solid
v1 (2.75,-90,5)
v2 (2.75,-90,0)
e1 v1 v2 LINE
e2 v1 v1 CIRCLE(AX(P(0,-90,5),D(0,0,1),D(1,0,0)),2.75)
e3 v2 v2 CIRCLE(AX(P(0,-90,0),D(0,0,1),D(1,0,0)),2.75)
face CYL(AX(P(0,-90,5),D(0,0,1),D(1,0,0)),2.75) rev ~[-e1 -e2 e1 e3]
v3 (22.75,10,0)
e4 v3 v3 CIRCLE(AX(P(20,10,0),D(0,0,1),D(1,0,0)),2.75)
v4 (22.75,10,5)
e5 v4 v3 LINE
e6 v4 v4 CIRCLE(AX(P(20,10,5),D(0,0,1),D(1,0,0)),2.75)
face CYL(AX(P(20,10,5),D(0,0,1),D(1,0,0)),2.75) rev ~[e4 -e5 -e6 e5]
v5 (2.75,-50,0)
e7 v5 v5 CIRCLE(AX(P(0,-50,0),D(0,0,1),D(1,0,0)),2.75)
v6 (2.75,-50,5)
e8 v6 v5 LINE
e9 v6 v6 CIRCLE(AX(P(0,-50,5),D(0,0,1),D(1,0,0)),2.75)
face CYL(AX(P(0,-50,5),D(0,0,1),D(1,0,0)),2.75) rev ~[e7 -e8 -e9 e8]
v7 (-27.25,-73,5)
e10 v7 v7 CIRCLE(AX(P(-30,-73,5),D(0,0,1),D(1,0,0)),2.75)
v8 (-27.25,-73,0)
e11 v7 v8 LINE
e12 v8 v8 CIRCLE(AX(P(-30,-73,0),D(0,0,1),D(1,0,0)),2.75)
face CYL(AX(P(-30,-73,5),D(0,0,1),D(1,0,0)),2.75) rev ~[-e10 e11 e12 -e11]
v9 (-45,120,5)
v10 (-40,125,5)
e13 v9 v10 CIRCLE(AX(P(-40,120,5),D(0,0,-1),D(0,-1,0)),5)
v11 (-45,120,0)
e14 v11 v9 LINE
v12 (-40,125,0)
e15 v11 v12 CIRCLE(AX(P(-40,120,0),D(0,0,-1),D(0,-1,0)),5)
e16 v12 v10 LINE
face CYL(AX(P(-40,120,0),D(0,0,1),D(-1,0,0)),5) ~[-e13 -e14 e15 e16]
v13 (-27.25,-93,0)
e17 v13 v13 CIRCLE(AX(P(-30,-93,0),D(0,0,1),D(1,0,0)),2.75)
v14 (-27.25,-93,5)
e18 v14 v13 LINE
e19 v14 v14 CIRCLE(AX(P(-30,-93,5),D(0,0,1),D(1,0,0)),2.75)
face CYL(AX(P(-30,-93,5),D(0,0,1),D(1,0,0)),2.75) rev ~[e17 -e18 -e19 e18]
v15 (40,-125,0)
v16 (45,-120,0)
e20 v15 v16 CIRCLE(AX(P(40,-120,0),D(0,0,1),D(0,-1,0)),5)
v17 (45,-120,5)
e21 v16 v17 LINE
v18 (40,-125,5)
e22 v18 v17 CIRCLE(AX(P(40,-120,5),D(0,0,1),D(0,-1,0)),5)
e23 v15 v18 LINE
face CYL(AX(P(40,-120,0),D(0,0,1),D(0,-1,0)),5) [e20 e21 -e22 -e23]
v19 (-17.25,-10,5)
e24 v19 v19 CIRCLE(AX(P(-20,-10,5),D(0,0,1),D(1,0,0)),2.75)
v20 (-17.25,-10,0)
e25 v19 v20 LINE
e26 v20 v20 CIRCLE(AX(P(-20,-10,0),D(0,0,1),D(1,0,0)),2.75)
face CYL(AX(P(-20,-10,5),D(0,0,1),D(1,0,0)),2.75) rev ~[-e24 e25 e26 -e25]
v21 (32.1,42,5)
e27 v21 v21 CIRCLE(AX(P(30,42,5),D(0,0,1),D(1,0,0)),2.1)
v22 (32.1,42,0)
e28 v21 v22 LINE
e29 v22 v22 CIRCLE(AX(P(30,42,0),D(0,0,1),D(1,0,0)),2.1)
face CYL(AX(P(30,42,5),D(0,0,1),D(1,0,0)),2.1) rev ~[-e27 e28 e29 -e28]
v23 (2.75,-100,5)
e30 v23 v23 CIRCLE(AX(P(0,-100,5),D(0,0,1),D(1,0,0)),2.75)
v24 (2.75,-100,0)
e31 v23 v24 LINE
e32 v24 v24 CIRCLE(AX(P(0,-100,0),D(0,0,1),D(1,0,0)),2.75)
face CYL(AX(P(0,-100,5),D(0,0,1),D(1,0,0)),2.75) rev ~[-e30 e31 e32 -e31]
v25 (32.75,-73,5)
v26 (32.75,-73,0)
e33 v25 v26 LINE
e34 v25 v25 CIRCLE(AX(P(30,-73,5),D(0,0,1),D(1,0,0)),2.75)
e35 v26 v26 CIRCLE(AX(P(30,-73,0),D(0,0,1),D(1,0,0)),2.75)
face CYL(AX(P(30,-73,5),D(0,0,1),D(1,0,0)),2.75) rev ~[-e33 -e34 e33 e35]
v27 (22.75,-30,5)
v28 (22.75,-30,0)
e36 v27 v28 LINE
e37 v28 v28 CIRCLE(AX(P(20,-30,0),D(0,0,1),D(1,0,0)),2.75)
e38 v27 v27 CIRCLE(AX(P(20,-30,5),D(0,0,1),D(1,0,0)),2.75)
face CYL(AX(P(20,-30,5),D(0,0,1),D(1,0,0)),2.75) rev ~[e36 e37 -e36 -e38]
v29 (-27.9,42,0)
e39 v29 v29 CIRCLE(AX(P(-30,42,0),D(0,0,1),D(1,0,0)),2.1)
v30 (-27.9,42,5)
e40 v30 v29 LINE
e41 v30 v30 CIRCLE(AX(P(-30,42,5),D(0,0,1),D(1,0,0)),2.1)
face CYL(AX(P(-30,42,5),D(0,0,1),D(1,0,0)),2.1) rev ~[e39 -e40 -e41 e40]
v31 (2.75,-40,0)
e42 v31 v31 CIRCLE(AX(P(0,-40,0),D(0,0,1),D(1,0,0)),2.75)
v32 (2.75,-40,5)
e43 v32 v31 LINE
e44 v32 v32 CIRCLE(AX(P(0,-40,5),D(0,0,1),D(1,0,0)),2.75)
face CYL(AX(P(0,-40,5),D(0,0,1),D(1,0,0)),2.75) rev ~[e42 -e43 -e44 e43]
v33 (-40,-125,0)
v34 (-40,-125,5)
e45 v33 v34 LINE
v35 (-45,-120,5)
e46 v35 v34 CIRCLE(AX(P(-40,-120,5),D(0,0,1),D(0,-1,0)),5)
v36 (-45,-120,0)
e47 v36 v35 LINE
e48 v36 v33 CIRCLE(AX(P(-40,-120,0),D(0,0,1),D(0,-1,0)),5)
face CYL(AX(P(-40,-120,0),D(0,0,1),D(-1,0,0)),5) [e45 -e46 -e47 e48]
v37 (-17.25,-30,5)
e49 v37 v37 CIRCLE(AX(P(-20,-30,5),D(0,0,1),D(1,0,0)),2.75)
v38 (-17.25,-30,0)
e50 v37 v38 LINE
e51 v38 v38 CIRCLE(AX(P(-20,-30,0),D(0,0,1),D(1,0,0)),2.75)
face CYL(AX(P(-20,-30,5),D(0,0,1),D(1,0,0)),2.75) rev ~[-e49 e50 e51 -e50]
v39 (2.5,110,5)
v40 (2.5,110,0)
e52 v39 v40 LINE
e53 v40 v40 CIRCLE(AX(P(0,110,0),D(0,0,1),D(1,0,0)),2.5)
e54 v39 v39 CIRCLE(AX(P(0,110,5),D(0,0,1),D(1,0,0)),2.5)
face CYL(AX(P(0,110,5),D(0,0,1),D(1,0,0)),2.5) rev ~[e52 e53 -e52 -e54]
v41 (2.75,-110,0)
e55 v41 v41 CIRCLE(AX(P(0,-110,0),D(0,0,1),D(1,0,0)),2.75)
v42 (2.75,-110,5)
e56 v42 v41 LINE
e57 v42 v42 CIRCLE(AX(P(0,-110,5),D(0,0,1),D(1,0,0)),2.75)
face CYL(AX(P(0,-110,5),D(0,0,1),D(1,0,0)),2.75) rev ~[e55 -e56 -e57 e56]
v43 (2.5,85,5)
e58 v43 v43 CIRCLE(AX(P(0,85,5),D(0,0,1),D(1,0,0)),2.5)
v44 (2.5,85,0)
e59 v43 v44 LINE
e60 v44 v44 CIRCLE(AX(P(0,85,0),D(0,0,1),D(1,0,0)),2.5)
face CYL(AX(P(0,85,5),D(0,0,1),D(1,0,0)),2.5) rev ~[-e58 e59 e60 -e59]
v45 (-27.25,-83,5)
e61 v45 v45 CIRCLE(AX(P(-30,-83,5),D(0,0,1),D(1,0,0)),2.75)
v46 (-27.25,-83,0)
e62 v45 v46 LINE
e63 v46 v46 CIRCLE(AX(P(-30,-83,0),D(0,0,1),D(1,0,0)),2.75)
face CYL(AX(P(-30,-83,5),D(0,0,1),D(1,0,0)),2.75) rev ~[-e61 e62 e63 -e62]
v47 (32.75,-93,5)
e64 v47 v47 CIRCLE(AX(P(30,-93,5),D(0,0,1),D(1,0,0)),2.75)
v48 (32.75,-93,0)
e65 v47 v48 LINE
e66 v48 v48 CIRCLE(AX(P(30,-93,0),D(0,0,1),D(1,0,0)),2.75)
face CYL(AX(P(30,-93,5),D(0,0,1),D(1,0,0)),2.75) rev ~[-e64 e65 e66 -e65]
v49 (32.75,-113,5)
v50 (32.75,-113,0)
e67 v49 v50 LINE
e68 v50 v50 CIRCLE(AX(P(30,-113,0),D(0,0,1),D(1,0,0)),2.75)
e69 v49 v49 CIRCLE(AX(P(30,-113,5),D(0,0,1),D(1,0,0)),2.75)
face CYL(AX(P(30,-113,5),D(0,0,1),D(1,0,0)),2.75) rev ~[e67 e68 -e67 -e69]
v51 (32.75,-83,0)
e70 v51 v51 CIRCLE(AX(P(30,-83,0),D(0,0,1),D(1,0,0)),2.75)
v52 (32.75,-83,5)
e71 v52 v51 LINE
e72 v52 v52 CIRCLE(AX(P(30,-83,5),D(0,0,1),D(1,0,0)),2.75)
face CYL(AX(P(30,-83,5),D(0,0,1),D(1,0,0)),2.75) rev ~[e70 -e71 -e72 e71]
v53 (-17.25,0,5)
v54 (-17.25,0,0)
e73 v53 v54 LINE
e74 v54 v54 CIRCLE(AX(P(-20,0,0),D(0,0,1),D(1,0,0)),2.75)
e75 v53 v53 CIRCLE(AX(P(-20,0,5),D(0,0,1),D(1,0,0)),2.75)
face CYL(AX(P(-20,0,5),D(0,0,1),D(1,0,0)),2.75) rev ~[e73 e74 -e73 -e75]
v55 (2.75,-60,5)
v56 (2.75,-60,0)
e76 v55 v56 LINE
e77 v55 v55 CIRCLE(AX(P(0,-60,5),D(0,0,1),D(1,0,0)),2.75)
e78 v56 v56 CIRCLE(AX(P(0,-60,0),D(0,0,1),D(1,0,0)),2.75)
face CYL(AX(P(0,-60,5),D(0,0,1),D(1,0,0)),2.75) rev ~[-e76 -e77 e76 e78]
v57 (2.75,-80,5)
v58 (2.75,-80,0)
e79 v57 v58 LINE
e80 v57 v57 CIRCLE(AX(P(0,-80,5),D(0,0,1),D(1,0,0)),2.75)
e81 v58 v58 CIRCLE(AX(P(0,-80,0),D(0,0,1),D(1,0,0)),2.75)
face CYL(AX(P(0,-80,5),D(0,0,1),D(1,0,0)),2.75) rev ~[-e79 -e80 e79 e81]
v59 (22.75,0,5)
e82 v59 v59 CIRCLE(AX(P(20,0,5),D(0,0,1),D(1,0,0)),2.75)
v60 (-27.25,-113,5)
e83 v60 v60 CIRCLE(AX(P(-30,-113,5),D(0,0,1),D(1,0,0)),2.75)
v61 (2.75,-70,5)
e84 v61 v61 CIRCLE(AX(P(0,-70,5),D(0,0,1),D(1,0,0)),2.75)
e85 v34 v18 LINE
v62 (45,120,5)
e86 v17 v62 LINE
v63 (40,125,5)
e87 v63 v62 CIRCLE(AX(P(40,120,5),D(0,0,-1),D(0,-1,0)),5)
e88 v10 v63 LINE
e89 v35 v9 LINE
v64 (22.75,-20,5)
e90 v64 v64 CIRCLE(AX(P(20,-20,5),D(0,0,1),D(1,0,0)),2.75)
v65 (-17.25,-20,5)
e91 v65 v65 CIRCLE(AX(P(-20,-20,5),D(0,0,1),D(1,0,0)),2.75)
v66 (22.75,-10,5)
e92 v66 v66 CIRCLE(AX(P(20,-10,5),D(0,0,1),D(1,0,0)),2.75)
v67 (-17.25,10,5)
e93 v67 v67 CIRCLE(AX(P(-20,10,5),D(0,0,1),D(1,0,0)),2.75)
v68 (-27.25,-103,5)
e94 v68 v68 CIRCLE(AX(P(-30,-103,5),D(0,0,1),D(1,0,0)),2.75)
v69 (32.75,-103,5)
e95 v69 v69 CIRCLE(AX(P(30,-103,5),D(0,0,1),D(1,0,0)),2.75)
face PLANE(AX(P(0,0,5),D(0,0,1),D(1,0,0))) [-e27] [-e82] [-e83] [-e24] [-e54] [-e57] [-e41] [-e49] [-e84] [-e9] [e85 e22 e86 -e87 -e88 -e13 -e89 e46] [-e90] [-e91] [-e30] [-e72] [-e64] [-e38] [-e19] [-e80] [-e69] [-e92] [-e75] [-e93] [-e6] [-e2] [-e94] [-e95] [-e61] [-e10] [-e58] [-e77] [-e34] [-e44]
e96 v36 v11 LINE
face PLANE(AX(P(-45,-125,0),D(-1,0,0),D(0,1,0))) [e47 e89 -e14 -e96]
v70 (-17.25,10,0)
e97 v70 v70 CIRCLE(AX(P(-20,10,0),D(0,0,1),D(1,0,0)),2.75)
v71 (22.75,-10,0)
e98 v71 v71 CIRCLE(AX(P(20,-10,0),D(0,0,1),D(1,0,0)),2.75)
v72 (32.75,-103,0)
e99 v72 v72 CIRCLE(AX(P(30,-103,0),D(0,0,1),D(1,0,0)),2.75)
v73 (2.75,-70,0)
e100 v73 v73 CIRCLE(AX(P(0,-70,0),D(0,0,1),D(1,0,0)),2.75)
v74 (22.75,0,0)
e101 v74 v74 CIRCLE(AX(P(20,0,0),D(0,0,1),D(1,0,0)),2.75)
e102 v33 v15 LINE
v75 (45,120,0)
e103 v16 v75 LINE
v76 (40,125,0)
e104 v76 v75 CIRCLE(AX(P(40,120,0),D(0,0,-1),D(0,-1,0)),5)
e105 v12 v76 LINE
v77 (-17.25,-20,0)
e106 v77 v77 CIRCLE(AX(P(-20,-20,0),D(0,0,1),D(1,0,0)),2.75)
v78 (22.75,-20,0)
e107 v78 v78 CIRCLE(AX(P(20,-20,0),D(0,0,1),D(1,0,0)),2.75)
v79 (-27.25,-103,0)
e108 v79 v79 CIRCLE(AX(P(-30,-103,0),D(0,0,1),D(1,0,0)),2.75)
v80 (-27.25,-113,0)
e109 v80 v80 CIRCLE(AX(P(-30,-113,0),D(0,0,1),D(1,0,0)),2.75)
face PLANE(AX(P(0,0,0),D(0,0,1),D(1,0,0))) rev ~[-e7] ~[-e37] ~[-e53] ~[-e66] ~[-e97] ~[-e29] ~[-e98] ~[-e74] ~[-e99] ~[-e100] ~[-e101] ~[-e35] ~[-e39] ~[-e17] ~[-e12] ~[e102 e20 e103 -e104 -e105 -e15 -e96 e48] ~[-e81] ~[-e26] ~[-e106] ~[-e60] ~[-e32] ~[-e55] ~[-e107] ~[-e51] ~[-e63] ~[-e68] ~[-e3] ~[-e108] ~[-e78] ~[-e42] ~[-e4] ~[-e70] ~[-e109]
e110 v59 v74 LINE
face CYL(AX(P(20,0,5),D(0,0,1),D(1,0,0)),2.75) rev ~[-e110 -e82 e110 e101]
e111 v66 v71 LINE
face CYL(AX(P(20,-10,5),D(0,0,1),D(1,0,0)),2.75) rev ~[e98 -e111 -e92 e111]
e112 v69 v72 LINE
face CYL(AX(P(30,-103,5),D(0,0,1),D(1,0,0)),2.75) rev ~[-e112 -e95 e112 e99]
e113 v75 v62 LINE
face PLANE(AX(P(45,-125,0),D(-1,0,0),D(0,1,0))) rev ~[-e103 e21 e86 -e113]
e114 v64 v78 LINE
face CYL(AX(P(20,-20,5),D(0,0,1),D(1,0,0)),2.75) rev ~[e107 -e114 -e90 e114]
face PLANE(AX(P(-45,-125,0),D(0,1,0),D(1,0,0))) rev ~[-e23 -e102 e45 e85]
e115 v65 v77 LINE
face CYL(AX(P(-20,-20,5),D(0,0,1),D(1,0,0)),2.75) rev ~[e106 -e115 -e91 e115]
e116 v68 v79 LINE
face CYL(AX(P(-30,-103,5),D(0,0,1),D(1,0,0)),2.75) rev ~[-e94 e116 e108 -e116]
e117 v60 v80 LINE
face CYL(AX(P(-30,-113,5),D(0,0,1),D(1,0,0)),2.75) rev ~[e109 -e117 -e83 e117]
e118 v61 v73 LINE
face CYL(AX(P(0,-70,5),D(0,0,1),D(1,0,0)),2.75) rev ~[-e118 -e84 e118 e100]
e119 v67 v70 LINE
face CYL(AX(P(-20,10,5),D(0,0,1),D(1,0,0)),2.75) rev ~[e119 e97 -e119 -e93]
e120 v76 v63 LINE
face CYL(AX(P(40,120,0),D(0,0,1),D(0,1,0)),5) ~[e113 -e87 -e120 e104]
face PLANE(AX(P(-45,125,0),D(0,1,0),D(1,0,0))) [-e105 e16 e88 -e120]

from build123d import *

# Parameters (mm, degrees)
SKETCH_1_W          = 90
SKETCH_1_H          = 250
EXTRUDE_1_DEPTH     = 5
SKETCH_2_R          = 2.5
SKETCH_2_R_2        = 2.1
CUT_EXTRUDE_1_DEPTH = 5
SKETCH_3_R          = 2.75
CUT_EXTRUDE_2_DEPTH = 5
SKETCH_4_R          = 2.75
CUT_EXTRUDE_3_DEPTH = 5
FILLET_1_R          = 5


with BuildPart() as part:
    # 草图1 → 凸台-拉伸1 (new body)
    with BuildSketch(Plane.XY):
        Rectangle(SKETCH_1_W, SKETCH_1_H)
    extrude(amount=EXTRUDE_1_DEPTH)

    # 草图2 → 切除-拉伸1 (cut)
    with BuildSketch(Plane.XY.offset(5)):
        with Locations((0, 110)):
            Circle(SKETCH_2_R)
        with Locations((0, 85)):
            Circle(SKETCH_2_R)
        with Locations((-30, 42)):
            Circle(SKETCH_2_R_2)
        with Locations((30, 42)):
            Circle(SKETCH_2_R_2)
    extrude(amount=-CUT_EXTRUDE_1_DEPTH, mode=Mode.SUBTRACT)

    # 草图3 → 切除-拉伸2 (cut)
    with BuildSketch(Plane.XY.offset(5)):
        with Locations((-20, -30)):
            Circle(SKETCH_3_R)
        with Locations((20, -30)):
            Circle(SKETCH_3_R)
        with Locations((0, -80)):
            Circle(SKETCH_3_R)
        with Locations((0, -70)):
            Circle(SKETCH_3_R)
        with Locations((0, -60)):
            Circle(SKETCH_3_R)
        with Locations((0, -50)):
            Circle(SKETCH_3_R)
        with Locations((0, -40)):
            Circle(SKETCH_3_R)
        with Locations((0, -90)):
            Circle(SKETCH_3_R)
        with Locations((0, -100)):
            Circle(SKETCH_3_R)
        with Locations((0, -110)):
            Circle(SKETCH_3_R)
        with Locations((-20, -20)):
            Circle(SKETCH_3_R)
        with Locations((20, -20)):
            Circle(SKETCH_3_R)
        with Locations((-20, -10)):
            Circle(SKETCH_3_R)
        with Locations((20, -10)):
            Circle(SKETCH_3_R)
        with Locations((-20, 0)):
            Circle(SKETCH_3_R)
        with Locations((20, 0)):
            Circle(SKETCH_3_R)
        with Locations((-20, 10)):
            Circle(SKETCH_3_R)
        with Locations((20, 10)):
            Circle(SKETCH_3_R)
    extrude(amount=-CUT_EXTRUDE_2_DEPTH, mode=Mode.SUBTRACT)

    # 草图4 → 切除-拉伸3 (cut)
    with BuildSketch(Plane.XY.offset(5)):
        with Locations((-30, -113)):
            Circle(SKETCH_4_R)
        with Locations((30, -113)):
            Circle(SKETCH_4_R)
        with Locations((-30, -103)):
            Circle(SKETCH_4_R)
        with Locations((30, -103)):
            Circle(SKETCH_4_R)
        with Locations((-30, -93)):
            Circle(SKETCH_4_R)
        with Locations((30, -93)):
            Circle(SKETCH_4_R)
        with Locations((-30, -83)):
            Circle(SKETCH_4_R)
        with Locations((30, -83)):
            Circle(SKETCH_4_R)
        with Locations((-30, -73)):
            Circle(SKETCH_4_R)
        with Locations((30, -73)):
            Circle(SKETCH_4_R)
    extrude(amount=-CUT_EXTRUDE_3_DEPTH, mode=Mode.SUBTRACT)

    # 圆角1
    fillet_1_edges = [part.edges().sort_by_distance(p)[0] for p in [
        (45, -125, 2.5),
        (-45, -125, 2.5),
        (-45, 125, 2.5),
        (45, 125, 2.5),
    ]]
    fillet(fillet_1_edges, radius=FILLET_1_R)


solid = part.part
